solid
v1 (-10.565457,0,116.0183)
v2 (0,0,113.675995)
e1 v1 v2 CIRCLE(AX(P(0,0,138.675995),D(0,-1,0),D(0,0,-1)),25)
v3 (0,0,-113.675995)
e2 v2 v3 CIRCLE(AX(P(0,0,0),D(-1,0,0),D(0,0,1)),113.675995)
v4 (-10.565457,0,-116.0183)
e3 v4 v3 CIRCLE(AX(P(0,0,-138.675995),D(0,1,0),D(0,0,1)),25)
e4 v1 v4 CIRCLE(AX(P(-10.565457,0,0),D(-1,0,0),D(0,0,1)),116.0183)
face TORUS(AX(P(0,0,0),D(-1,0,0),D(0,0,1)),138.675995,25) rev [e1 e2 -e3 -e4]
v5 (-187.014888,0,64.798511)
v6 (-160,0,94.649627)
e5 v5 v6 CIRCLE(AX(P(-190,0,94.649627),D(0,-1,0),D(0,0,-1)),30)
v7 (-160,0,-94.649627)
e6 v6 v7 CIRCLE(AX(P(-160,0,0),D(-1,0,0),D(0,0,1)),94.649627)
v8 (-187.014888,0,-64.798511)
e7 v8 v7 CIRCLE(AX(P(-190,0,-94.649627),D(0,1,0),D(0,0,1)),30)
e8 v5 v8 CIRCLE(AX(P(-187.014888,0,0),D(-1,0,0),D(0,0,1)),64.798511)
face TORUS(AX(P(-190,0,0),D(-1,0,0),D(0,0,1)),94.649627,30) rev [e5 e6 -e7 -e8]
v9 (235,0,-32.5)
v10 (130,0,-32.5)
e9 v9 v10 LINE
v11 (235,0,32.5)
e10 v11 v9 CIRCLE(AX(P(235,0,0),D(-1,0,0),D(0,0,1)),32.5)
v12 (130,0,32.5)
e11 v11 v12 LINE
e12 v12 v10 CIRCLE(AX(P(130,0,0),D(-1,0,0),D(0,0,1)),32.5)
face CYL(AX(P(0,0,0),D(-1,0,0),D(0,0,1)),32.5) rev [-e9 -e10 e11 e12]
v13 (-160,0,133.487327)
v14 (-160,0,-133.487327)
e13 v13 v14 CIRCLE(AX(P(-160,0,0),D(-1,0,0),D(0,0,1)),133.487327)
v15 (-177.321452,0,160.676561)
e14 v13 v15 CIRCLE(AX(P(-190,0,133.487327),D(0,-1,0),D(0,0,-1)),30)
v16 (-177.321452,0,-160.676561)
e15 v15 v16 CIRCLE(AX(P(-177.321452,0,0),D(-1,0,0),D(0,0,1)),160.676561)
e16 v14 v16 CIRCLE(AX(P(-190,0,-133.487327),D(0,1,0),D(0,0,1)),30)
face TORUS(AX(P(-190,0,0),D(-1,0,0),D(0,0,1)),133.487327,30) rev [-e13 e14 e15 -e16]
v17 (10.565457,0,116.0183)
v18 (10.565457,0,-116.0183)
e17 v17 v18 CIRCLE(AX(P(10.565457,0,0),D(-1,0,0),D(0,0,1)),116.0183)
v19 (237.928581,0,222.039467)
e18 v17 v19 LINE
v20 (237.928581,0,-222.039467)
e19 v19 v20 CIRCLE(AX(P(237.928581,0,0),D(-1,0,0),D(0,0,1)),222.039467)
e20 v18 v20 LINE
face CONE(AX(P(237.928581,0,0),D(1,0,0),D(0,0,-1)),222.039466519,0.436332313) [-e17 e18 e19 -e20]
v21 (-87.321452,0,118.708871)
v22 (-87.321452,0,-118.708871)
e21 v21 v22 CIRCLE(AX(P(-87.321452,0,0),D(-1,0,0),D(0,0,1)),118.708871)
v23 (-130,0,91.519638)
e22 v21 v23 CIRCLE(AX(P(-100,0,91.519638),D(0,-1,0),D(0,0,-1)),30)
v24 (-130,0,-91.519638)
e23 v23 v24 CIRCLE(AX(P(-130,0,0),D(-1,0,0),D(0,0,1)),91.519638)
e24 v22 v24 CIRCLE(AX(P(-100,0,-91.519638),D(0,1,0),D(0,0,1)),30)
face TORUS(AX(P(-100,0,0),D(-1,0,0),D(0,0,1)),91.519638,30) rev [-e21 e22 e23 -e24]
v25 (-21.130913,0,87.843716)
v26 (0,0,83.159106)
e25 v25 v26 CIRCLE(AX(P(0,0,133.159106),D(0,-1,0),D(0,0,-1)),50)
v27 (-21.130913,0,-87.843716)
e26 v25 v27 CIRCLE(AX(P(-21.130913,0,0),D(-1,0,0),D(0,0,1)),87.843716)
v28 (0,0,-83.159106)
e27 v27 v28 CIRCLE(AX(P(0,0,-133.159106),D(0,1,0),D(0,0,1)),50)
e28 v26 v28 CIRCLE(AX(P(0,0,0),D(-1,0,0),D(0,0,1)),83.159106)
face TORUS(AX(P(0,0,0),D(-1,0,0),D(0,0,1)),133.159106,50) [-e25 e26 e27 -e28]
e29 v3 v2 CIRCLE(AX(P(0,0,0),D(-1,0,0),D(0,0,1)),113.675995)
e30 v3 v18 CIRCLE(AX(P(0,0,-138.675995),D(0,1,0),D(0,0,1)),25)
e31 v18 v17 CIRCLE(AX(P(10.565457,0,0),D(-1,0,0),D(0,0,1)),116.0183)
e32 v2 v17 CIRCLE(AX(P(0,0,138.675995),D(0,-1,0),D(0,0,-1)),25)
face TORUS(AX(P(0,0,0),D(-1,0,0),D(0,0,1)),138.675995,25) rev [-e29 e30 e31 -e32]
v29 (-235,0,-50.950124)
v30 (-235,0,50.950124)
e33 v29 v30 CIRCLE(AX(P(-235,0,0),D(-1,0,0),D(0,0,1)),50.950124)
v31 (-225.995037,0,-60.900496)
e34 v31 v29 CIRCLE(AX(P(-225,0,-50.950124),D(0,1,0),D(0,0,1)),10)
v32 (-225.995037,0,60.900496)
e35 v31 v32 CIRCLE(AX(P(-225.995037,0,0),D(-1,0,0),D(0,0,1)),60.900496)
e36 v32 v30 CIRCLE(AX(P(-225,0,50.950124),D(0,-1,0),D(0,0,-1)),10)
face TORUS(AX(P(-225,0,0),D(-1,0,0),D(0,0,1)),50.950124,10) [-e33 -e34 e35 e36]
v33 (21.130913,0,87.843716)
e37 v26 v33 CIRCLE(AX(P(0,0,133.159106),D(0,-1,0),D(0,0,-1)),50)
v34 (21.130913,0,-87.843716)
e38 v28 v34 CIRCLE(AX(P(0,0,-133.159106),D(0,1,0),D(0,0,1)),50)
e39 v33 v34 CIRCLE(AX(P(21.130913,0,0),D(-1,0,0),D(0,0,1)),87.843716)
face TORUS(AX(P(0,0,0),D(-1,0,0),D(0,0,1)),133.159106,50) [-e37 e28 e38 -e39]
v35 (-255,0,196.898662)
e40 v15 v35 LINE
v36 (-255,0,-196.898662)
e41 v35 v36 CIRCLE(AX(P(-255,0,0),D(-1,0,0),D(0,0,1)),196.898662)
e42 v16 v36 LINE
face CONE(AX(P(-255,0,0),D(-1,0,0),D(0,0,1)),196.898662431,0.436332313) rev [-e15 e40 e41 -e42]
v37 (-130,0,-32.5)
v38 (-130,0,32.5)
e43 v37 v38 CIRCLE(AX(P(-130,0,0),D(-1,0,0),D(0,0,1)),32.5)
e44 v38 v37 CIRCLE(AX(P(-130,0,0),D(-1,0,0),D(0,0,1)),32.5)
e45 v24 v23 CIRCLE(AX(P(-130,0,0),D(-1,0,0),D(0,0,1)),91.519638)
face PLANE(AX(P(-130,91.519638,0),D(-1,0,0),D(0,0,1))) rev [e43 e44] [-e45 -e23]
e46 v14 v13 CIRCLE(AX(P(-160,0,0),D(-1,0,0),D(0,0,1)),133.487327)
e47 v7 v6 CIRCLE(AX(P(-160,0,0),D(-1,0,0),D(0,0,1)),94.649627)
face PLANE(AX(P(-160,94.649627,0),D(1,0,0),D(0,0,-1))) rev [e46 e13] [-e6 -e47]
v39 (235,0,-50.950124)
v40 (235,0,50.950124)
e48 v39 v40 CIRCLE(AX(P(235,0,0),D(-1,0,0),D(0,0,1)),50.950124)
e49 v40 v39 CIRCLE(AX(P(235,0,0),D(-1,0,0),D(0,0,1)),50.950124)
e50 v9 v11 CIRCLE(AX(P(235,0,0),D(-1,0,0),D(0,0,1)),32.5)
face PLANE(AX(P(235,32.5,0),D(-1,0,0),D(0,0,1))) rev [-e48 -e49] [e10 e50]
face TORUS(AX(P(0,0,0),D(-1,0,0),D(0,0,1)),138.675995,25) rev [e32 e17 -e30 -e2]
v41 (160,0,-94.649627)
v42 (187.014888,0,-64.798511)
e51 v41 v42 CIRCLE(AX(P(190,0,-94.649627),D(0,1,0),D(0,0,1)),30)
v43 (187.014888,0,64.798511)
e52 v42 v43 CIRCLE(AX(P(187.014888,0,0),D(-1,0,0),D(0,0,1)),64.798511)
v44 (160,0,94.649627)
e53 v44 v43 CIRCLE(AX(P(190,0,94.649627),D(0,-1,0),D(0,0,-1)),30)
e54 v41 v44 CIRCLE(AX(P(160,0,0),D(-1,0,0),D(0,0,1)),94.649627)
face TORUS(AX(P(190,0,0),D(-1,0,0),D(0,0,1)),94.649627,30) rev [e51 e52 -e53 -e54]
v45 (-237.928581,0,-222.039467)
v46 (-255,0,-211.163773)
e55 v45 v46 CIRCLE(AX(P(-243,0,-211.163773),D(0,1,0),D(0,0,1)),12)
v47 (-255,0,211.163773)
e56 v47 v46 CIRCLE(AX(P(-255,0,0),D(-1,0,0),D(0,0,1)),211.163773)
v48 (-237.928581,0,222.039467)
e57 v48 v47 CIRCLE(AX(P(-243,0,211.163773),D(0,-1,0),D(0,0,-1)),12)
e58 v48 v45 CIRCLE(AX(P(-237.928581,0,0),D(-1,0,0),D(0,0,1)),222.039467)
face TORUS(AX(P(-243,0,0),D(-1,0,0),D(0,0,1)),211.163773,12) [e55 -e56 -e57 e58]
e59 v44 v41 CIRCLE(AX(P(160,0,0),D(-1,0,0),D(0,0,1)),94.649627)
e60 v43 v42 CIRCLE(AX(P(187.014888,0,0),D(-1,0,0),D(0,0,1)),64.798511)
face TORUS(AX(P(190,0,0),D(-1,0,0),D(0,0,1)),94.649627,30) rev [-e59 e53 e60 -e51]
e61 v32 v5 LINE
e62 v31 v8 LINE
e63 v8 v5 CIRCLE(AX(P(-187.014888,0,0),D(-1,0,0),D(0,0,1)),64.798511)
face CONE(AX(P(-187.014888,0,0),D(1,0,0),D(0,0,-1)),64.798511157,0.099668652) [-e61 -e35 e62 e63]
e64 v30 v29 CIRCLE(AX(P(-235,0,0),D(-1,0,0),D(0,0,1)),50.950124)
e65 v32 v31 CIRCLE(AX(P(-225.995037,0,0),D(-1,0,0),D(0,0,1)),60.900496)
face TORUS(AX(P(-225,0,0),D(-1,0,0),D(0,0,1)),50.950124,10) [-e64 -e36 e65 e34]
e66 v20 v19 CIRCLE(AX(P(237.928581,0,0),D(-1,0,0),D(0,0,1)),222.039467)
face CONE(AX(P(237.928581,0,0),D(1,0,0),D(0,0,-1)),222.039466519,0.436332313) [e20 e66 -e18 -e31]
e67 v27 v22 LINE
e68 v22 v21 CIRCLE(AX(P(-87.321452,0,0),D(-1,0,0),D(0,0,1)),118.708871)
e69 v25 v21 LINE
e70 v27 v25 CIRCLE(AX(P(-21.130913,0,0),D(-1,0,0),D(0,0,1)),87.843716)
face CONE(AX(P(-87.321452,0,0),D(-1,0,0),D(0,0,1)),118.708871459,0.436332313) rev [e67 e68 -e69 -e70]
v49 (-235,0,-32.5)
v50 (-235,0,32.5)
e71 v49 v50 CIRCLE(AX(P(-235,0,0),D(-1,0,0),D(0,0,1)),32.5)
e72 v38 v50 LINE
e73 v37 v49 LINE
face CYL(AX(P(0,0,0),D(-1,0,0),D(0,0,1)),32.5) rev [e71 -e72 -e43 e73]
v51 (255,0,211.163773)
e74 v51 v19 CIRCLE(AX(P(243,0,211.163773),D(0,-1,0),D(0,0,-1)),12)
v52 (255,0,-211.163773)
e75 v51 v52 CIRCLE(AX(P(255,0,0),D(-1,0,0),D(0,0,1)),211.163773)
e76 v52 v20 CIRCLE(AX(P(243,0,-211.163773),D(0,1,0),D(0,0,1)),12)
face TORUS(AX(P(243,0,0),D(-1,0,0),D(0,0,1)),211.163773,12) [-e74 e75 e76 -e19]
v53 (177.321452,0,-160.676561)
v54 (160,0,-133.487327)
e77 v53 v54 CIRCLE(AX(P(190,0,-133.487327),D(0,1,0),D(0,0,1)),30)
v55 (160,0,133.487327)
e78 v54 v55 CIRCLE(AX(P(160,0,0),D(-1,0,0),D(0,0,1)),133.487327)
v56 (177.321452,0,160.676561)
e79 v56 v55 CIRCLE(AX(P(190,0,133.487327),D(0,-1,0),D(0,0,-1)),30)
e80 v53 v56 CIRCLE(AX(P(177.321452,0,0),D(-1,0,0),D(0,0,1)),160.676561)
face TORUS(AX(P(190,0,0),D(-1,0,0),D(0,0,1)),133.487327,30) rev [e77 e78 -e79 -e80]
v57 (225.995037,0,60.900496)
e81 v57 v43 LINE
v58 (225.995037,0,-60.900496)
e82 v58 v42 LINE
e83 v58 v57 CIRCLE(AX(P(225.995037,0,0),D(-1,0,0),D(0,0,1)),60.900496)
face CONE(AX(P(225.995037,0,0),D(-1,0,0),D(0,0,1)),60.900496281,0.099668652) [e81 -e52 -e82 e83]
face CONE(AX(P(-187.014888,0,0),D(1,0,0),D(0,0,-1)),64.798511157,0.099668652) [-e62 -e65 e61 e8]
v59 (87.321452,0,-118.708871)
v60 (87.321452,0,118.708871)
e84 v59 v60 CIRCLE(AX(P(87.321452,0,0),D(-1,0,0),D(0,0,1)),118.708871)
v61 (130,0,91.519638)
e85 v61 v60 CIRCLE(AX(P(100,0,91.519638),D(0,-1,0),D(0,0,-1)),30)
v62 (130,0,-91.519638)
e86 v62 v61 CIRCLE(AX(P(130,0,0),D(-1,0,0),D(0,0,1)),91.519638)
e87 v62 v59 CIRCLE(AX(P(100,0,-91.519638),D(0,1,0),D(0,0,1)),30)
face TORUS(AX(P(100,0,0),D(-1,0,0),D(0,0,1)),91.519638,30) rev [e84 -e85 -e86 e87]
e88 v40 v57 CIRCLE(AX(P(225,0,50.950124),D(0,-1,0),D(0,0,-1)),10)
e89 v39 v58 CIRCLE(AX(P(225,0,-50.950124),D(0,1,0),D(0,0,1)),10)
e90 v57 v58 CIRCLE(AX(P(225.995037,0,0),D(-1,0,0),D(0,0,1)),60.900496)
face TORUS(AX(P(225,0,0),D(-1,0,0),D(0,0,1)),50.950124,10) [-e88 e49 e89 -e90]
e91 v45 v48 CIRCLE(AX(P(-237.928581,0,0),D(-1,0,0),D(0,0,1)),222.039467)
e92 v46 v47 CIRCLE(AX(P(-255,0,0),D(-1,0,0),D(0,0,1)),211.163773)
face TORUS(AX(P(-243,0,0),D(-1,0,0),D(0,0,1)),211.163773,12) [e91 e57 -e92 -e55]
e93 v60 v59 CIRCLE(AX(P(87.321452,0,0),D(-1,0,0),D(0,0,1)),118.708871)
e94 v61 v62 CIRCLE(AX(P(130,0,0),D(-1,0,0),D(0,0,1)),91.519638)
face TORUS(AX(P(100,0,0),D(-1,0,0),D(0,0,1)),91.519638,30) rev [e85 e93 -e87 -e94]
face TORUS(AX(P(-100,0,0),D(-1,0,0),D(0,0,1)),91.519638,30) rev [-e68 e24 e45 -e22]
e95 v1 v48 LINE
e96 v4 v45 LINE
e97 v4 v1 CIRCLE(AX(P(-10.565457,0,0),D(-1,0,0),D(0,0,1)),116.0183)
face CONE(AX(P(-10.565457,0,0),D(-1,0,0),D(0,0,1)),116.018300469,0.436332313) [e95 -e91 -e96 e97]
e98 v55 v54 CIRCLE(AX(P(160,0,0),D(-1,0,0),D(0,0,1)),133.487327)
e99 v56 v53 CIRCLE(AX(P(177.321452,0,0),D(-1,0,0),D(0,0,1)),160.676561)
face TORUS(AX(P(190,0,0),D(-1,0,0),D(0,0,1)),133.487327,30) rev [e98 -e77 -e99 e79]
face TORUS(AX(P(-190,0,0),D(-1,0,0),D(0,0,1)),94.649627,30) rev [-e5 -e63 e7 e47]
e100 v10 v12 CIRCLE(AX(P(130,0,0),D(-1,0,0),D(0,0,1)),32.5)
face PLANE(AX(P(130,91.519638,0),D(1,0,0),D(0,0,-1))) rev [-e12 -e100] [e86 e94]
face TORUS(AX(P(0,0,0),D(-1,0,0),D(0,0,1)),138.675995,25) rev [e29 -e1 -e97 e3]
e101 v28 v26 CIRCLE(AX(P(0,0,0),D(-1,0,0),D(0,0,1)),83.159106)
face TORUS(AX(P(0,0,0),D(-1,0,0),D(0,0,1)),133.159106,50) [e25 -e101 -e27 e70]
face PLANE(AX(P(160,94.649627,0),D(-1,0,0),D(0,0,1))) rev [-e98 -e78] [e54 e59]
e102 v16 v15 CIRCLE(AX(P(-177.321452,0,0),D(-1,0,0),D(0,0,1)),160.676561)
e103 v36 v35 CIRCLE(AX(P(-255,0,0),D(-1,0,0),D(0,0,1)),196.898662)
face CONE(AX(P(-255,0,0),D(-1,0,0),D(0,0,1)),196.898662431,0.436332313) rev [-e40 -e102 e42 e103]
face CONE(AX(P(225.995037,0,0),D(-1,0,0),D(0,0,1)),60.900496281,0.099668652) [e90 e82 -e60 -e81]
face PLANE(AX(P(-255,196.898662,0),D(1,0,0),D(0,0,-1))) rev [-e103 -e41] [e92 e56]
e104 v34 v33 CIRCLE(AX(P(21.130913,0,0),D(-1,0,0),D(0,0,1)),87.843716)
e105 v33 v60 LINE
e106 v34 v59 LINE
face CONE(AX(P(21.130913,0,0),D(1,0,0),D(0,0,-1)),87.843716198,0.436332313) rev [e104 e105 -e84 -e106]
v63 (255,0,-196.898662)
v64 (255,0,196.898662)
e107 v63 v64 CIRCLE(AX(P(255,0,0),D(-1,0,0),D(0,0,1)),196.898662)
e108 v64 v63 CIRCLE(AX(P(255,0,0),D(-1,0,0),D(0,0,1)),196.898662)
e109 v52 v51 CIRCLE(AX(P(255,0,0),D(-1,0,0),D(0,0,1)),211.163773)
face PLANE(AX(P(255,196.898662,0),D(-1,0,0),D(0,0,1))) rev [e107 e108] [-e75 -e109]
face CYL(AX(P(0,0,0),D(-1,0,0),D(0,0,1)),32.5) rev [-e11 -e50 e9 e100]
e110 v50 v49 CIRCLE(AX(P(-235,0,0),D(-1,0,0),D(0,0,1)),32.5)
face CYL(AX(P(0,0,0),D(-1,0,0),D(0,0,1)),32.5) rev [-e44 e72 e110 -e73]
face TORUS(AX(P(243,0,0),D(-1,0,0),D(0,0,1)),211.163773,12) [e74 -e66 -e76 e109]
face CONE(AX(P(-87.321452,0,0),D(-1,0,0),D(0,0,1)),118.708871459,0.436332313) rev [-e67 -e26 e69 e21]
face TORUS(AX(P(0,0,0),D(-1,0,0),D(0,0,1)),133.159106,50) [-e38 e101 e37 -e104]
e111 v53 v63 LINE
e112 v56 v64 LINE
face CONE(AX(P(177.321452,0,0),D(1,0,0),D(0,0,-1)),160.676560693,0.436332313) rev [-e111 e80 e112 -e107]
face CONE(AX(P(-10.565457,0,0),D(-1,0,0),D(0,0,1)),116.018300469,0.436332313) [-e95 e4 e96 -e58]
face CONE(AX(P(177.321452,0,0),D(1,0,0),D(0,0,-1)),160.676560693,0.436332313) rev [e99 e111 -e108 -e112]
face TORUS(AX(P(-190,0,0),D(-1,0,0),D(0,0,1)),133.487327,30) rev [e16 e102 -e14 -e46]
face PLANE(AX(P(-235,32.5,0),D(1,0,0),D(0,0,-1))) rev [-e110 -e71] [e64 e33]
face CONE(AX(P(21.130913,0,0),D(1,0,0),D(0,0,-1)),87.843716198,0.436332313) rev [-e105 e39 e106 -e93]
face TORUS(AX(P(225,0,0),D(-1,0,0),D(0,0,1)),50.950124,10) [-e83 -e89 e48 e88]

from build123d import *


with BuildPart() as part:
    # Pulley Profile Sketch → Pulley Body Revolve (revolve)
    with BuildSketch(Plane.XY, mode=Mode.PRIVATE) as pulley_body_revolve_sk:
        with BuildLine():
            Line((130, 32.5), (235, 32.5))
            Line((235, 32.5), (235, 50.950124379))
            ThreePointArc((235, 50.950124379), (232.414525336, 57.660177586), (225.99503719, 60.900496281))
            Line((225.99503719, 60.900496281), (187.014888429, 64.798511157))
            ThreePointArc((187.014888429, 64.798511157), (167.756423993, 74.519467241), (160, 94.649626863))
            Line((160, 94.649626863), (160, 133.487327082))
            ThreePointArc((160, 133.487327082), (164.698256626, 149.606315333), (177.321452148, 160.676560693))
            Line((177.321452148, 160.676560693), (255, 196.898662431))
            Line((255, 196.898662431), (255, 211.163773075))
            ThreePointArc((255, 211.163773075), (249.4475953, 221.284470424), (237.928580859, 222.039466519))
            Line((237.928580859, 222.039466519), (10.565456544, 116.018300469))
            ThreePointArc((10.565456544, 116.018300469), (0, 113.675995145), (-10.565456544, 116.018300469))
            Line((-10.565456544, 116.018300469), (-237.928580859, 222.039466519))
            ThreePointArc((-237.928580859, 222.039466519), (-249.4475953, 221.284470424), (-255, 211.163773075))
            Line((-255, 211.163773075), (-255, 196.898662431))
            Line((-255, 196.898662431), (-177.321452148, 160.676560693))
            ThreePointArc((-177.321452148, 160.676560693), (-164.698256626, 149.606315333), (-160, 133.487327082))
            Line((-160, 133.487327082), (-160, 94.649626863))
            ThreePointArc((-160, 94.649626863), (-167.756423993, 74.519467241), (-187.014888429, 64.798511157))
            Line((-187.014888429, 64.798511157), (-225.99503719, 60.900496281))
            ThreePointArc((-225.99503719, 60.900496281), (-232.414525336, 57.660177586), (-235, 50.950124379))
            Line((-235, 50.950124379), (-235, 32.5))
            Line((-235, 32.5), (-130, 32.5))
            Line((-130, 32.5), (-130, 91.519637848))
            ThreePointArc((-130, 91.519637848), (-116.11898825, 116.821381223), (-87.321452148, 118.708871459))
            Line((-87.321452148, 118.708871459), (-21.130913087, 87.843716198))
            ThreePointArc((-21.130913087, 87.843716198), (0, 83.15910555), (21.130913087, 87.843716198))
            Line((21.130913087, 87.843716198), (87.321452148, 118.708871459))
            ThreePointArc((87.321452148, 118.708871459), (116.11898825, 116.821381223), (130, 91.519637848))
            Line((130, 91.519637848), (130, 32.5))
        make_face()
    revolve(pulley_body_revolve_sk.sketch.rotate(Axis((0, 0, 0), (1, 0, 0)), 90), axis=Axis((0, 0, 0), (1, 0, 0)))


solid = part.part
